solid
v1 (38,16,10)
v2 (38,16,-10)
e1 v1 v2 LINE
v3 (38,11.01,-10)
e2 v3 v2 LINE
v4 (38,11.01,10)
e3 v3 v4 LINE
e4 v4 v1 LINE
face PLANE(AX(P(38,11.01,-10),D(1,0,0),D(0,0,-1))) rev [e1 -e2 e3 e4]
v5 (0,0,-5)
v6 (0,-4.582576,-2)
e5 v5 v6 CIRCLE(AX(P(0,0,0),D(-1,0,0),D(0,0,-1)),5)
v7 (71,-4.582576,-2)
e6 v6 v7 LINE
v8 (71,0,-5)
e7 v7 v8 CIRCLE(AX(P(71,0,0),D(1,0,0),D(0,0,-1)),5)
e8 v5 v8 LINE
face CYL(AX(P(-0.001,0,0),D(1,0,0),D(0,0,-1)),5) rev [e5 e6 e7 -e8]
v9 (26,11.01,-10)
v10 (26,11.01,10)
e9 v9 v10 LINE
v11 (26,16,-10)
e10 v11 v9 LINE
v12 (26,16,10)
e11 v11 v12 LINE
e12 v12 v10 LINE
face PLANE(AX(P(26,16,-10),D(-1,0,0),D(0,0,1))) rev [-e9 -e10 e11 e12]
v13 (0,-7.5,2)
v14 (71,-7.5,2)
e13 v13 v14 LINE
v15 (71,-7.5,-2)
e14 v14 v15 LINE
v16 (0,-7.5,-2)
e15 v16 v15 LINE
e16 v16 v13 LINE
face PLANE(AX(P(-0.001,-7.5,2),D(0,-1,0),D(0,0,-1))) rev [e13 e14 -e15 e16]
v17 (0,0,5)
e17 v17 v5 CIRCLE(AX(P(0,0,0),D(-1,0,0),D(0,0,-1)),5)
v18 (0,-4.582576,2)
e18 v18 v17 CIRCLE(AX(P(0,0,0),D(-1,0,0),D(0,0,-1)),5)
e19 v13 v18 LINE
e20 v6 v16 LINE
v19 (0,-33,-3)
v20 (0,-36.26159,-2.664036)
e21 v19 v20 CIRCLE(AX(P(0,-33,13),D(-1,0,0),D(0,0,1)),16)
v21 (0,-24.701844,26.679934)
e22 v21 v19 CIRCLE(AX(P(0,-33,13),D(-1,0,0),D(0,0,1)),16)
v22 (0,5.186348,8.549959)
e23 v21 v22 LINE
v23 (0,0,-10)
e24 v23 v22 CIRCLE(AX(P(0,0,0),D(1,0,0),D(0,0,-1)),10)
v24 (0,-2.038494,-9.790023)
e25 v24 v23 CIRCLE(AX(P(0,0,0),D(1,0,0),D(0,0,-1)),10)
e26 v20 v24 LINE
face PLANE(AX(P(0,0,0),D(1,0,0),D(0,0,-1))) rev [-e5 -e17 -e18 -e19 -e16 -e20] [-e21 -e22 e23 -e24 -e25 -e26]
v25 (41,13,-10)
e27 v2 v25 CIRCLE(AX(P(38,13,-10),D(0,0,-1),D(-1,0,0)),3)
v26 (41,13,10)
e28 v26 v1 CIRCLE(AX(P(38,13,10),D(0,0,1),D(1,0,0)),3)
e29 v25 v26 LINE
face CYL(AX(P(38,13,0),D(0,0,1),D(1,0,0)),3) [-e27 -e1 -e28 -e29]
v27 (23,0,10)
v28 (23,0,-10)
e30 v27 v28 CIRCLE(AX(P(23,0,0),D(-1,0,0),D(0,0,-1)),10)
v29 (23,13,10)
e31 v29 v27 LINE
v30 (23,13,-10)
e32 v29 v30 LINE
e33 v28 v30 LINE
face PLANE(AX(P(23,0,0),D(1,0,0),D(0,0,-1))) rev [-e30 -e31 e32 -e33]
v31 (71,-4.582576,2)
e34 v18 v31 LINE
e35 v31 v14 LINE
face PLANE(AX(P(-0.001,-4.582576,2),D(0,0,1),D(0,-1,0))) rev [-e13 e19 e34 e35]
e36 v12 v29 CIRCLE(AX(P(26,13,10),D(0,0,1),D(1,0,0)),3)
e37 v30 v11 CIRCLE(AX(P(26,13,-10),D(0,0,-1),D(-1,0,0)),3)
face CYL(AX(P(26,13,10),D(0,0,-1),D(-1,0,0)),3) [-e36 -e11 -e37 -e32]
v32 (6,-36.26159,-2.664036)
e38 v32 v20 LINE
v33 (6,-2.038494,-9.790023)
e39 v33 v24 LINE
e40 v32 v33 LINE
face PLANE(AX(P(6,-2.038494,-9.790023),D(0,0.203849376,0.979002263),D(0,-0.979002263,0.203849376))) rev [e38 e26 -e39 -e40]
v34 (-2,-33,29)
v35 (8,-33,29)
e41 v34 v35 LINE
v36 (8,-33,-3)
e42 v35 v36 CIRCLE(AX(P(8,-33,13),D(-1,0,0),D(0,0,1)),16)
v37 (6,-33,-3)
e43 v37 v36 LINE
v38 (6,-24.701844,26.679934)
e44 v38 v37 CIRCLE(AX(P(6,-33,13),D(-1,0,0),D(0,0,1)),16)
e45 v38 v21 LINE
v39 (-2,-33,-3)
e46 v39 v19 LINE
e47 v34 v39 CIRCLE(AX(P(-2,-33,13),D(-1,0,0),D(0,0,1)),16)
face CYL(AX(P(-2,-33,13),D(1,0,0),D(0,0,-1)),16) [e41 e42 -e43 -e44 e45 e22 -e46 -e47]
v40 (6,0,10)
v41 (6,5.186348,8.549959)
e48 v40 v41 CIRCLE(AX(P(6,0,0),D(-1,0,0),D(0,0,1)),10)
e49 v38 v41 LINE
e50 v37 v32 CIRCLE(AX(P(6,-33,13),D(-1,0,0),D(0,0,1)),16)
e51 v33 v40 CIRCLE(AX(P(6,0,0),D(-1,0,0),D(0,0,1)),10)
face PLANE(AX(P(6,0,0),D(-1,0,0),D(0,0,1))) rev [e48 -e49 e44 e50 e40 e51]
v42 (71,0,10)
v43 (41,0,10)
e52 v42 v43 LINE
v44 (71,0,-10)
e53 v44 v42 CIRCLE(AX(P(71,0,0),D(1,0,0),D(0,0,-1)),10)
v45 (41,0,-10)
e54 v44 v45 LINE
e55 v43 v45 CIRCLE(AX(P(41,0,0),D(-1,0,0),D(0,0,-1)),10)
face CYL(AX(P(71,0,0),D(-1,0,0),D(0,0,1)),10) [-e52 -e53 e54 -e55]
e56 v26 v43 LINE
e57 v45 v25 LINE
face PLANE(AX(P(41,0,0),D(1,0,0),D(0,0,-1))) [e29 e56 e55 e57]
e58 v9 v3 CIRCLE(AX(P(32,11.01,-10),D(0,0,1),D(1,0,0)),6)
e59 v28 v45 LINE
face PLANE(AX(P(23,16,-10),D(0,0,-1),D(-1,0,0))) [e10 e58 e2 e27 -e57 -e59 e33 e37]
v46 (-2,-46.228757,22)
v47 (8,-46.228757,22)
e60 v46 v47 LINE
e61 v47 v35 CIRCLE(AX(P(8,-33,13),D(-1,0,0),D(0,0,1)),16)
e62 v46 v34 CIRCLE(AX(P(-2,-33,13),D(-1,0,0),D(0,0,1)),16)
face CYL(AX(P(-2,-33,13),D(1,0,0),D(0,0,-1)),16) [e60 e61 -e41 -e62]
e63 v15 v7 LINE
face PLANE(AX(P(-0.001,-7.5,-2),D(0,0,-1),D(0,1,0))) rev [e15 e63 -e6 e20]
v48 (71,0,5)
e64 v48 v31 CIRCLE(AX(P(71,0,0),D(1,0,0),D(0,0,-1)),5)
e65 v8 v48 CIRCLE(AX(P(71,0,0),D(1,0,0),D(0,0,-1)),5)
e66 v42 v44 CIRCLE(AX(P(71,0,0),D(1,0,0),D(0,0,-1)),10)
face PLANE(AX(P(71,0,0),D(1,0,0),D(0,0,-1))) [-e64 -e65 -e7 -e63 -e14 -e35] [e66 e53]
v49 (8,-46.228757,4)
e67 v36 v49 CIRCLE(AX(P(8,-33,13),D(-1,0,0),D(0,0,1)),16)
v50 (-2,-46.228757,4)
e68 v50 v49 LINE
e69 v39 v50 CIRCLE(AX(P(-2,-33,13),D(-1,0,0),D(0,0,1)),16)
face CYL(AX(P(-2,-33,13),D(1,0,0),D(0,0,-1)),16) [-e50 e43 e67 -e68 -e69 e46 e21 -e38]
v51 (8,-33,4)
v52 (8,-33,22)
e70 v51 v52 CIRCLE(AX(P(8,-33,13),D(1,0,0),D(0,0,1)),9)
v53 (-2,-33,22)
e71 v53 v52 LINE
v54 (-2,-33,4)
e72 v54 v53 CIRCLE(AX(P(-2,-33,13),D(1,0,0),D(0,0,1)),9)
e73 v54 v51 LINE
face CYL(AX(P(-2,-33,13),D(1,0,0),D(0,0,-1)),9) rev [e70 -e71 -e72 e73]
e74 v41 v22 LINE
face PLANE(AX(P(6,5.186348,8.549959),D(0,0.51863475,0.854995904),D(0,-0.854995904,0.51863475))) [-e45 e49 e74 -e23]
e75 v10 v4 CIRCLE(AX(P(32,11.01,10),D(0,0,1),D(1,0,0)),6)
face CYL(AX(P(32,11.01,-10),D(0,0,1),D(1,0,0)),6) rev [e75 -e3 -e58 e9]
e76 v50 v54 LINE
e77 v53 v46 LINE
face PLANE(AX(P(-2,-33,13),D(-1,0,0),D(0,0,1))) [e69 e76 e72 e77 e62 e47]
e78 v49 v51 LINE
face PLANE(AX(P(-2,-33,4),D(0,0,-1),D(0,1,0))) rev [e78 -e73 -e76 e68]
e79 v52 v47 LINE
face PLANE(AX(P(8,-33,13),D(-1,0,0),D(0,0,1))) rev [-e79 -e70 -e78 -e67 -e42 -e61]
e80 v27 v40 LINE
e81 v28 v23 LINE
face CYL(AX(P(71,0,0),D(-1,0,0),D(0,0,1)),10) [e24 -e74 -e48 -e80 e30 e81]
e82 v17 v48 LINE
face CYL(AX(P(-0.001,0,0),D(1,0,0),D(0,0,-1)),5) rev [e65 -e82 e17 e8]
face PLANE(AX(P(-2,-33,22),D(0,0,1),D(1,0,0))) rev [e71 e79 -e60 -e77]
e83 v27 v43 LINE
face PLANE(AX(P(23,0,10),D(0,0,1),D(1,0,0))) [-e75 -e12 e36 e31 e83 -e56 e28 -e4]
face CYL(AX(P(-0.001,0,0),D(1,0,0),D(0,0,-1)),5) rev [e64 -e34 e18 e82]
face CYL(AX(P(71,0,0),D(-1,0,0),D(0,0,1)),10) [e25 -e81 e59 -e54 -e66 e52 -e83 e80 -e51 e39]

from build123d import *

# Parameters (mm, degrees)
HUB_PROFILE_20_R        = 10
SHAFT_HUB_20X71_DEPTH   = 71
KEYED_BORE_10_REACH     = 74.395
ROCKER_START            = -48
ROCKER_ARM_DEPTH        = 18
ARM_FILLET_R3_R         = 3
SADDLE_BLOCK_DEPTH      = 2
SADDLE_BLOCK_DEPTH_BACK = 8
CONNECTING_WEB_DEPTH    = 6
FORK_SLOT_DEPTH         = 90.549416149
FORK_SLOT_DEPTH_BACK    = 90.549416149


with BuildPart() as part:
    # Hub Profile Ø20 → Shaft Hub Ø20x71 (new body)
    with BuildSketch(Plane(origin=(0, 0, 0), x_dir=(0, 0, -1), z_dir=(1, 0, 0))):
        Circle(HUB_PROFILE_20_R)
    extrude(amount=SHAFT_HUB_20X71_DEPTH)

    # Keyed Bore Profile → Keyed Bore Ø10 (cut, up to next)
    with BuildSketch(Plane(origin=(71, 0, 0), x_dir=(0, 0, -1), z_dir=(1, 0, 0)), mode=Mode.PRIVATE) as keyed_bore_10_sk1:
        with BuildLine():
            Line((-2, -4.582575695), (-2, -7.5))
            Line((-2, -7.5), (2, -7.5))
            Line((2, -7.5), (2, -4.582575695))
            ThreePointArc((2, -4.582575695), (0, 5), (-2, -4.582575695))
        make_face()
    keyed_bore_10_tool1 = extrude(keyed_bore_10_sk1.sketch, amount=-KEYED_BORE_10_REACH, mode=Mode.PRIVATE) & part.part
    add(keyed_bore_10_tool1.solids().sort_by_distance((71, -0.731497, 0))[0], mode=Mode.SUBTRACT)

    # Rocker Arm Profile → Rocker Arm (add)
    with BuildSketch(Plane(origin=(71, 0, 0), x_dir=(0, 0, -1), z_dir=(1, 0, 0)).offset(ROCKER_START)):
        with BuildLine():
            Line((-10, 0), (-10, 16))
            Line((-10, 16), (10, 16))
            Line((10, 16), (10, 0))
            ThreePointArc((10, 0), (0, 10), (-10, 0))
        make_face()
    extrude(amount=ROCKER_ARM_DEPTH)

    # Arm Fillet R3
    arm_fillet_r3_edges = [part.edges().sort_by_distance(p)[0] for p in [
        (23, 16, 0),
        (41, 16, 0),
    ]]
    fillet(arm_fillet_r3_edges, radius=ARM_FILLET_R3_R)



with BuildPart() as body_2:
    # Saddle Block Profile → Saddle Block (new, two sides: drawn at the far end of the back side and taken through both)
    with BuildSketch(Plane.ZY.offset(-SADDLE_BLOCK_DEPTH_BACK)):
        with BuildLine():
            Line((22, -33), (22, -46.228756555))
            ThreePointArc((22, -46.228756555), (13, -17), (4, -46.228756555))
            Line((4, -46.228756555), (4, -33))
            ThreePointArc((4, -33), (13, -24), (22, -33))
        make_face()
    extrude(amount=SADDLE_BLOCK_DEPTH + SADDLE_BLOCK_DEPTH_BACK)


with BuildPart() as part_1:
    add(part.part)

    add(body_2.part)  # Connecting Web merges body 2
    # Connecting Web Profile → Connecting Web (add)
    with BuildSketch(Plane.ZY):
        with BuildLine():
            ThreePointArc((-2.664036214, -36.261590024), (7.135607706, -18.113465715), (26.679934465, -24.701843999))
            Line((26.679934465, -24.701843999), (8.549959041, 5.186347501))
            ThreePointArc((8.549959041, 5.186347501), (9.63066951, 2.692620433), (10, 0))
            ThreePointArc((10, 0), (1.024639854, -9.947367148), (-9.790022634, -2.038493765))
            Line((-9.790022634, -2.038493765), (-2.664036214, -36.261590024))
        make_face()
    extrude(amount=-CONNECTING_WEB_DEPTH)

    # Fork Slot Profile → Fork Slot (cut, two sides: drawn at the far end of the back side and taken through both)
    with BuildSketch(Plane.XY.offset(-FORK_SLOT_DEPTH_BACK)):
        with BuildLine():
            Line((26, 16), (26, 11.01))
            ThreePointArc((26, 11.01), (32, 5.01), (38, 11.01))
            Line((38, 11.01), (38, 16))
            Line((38, 16), (26, 16))
        make_face()
    extrude(amount=FORK_SLOT_DEPTH + FORK_SLOT_DEPTH_BACK, mode=Mode.SUBTRACT)


solid = part_1.part
